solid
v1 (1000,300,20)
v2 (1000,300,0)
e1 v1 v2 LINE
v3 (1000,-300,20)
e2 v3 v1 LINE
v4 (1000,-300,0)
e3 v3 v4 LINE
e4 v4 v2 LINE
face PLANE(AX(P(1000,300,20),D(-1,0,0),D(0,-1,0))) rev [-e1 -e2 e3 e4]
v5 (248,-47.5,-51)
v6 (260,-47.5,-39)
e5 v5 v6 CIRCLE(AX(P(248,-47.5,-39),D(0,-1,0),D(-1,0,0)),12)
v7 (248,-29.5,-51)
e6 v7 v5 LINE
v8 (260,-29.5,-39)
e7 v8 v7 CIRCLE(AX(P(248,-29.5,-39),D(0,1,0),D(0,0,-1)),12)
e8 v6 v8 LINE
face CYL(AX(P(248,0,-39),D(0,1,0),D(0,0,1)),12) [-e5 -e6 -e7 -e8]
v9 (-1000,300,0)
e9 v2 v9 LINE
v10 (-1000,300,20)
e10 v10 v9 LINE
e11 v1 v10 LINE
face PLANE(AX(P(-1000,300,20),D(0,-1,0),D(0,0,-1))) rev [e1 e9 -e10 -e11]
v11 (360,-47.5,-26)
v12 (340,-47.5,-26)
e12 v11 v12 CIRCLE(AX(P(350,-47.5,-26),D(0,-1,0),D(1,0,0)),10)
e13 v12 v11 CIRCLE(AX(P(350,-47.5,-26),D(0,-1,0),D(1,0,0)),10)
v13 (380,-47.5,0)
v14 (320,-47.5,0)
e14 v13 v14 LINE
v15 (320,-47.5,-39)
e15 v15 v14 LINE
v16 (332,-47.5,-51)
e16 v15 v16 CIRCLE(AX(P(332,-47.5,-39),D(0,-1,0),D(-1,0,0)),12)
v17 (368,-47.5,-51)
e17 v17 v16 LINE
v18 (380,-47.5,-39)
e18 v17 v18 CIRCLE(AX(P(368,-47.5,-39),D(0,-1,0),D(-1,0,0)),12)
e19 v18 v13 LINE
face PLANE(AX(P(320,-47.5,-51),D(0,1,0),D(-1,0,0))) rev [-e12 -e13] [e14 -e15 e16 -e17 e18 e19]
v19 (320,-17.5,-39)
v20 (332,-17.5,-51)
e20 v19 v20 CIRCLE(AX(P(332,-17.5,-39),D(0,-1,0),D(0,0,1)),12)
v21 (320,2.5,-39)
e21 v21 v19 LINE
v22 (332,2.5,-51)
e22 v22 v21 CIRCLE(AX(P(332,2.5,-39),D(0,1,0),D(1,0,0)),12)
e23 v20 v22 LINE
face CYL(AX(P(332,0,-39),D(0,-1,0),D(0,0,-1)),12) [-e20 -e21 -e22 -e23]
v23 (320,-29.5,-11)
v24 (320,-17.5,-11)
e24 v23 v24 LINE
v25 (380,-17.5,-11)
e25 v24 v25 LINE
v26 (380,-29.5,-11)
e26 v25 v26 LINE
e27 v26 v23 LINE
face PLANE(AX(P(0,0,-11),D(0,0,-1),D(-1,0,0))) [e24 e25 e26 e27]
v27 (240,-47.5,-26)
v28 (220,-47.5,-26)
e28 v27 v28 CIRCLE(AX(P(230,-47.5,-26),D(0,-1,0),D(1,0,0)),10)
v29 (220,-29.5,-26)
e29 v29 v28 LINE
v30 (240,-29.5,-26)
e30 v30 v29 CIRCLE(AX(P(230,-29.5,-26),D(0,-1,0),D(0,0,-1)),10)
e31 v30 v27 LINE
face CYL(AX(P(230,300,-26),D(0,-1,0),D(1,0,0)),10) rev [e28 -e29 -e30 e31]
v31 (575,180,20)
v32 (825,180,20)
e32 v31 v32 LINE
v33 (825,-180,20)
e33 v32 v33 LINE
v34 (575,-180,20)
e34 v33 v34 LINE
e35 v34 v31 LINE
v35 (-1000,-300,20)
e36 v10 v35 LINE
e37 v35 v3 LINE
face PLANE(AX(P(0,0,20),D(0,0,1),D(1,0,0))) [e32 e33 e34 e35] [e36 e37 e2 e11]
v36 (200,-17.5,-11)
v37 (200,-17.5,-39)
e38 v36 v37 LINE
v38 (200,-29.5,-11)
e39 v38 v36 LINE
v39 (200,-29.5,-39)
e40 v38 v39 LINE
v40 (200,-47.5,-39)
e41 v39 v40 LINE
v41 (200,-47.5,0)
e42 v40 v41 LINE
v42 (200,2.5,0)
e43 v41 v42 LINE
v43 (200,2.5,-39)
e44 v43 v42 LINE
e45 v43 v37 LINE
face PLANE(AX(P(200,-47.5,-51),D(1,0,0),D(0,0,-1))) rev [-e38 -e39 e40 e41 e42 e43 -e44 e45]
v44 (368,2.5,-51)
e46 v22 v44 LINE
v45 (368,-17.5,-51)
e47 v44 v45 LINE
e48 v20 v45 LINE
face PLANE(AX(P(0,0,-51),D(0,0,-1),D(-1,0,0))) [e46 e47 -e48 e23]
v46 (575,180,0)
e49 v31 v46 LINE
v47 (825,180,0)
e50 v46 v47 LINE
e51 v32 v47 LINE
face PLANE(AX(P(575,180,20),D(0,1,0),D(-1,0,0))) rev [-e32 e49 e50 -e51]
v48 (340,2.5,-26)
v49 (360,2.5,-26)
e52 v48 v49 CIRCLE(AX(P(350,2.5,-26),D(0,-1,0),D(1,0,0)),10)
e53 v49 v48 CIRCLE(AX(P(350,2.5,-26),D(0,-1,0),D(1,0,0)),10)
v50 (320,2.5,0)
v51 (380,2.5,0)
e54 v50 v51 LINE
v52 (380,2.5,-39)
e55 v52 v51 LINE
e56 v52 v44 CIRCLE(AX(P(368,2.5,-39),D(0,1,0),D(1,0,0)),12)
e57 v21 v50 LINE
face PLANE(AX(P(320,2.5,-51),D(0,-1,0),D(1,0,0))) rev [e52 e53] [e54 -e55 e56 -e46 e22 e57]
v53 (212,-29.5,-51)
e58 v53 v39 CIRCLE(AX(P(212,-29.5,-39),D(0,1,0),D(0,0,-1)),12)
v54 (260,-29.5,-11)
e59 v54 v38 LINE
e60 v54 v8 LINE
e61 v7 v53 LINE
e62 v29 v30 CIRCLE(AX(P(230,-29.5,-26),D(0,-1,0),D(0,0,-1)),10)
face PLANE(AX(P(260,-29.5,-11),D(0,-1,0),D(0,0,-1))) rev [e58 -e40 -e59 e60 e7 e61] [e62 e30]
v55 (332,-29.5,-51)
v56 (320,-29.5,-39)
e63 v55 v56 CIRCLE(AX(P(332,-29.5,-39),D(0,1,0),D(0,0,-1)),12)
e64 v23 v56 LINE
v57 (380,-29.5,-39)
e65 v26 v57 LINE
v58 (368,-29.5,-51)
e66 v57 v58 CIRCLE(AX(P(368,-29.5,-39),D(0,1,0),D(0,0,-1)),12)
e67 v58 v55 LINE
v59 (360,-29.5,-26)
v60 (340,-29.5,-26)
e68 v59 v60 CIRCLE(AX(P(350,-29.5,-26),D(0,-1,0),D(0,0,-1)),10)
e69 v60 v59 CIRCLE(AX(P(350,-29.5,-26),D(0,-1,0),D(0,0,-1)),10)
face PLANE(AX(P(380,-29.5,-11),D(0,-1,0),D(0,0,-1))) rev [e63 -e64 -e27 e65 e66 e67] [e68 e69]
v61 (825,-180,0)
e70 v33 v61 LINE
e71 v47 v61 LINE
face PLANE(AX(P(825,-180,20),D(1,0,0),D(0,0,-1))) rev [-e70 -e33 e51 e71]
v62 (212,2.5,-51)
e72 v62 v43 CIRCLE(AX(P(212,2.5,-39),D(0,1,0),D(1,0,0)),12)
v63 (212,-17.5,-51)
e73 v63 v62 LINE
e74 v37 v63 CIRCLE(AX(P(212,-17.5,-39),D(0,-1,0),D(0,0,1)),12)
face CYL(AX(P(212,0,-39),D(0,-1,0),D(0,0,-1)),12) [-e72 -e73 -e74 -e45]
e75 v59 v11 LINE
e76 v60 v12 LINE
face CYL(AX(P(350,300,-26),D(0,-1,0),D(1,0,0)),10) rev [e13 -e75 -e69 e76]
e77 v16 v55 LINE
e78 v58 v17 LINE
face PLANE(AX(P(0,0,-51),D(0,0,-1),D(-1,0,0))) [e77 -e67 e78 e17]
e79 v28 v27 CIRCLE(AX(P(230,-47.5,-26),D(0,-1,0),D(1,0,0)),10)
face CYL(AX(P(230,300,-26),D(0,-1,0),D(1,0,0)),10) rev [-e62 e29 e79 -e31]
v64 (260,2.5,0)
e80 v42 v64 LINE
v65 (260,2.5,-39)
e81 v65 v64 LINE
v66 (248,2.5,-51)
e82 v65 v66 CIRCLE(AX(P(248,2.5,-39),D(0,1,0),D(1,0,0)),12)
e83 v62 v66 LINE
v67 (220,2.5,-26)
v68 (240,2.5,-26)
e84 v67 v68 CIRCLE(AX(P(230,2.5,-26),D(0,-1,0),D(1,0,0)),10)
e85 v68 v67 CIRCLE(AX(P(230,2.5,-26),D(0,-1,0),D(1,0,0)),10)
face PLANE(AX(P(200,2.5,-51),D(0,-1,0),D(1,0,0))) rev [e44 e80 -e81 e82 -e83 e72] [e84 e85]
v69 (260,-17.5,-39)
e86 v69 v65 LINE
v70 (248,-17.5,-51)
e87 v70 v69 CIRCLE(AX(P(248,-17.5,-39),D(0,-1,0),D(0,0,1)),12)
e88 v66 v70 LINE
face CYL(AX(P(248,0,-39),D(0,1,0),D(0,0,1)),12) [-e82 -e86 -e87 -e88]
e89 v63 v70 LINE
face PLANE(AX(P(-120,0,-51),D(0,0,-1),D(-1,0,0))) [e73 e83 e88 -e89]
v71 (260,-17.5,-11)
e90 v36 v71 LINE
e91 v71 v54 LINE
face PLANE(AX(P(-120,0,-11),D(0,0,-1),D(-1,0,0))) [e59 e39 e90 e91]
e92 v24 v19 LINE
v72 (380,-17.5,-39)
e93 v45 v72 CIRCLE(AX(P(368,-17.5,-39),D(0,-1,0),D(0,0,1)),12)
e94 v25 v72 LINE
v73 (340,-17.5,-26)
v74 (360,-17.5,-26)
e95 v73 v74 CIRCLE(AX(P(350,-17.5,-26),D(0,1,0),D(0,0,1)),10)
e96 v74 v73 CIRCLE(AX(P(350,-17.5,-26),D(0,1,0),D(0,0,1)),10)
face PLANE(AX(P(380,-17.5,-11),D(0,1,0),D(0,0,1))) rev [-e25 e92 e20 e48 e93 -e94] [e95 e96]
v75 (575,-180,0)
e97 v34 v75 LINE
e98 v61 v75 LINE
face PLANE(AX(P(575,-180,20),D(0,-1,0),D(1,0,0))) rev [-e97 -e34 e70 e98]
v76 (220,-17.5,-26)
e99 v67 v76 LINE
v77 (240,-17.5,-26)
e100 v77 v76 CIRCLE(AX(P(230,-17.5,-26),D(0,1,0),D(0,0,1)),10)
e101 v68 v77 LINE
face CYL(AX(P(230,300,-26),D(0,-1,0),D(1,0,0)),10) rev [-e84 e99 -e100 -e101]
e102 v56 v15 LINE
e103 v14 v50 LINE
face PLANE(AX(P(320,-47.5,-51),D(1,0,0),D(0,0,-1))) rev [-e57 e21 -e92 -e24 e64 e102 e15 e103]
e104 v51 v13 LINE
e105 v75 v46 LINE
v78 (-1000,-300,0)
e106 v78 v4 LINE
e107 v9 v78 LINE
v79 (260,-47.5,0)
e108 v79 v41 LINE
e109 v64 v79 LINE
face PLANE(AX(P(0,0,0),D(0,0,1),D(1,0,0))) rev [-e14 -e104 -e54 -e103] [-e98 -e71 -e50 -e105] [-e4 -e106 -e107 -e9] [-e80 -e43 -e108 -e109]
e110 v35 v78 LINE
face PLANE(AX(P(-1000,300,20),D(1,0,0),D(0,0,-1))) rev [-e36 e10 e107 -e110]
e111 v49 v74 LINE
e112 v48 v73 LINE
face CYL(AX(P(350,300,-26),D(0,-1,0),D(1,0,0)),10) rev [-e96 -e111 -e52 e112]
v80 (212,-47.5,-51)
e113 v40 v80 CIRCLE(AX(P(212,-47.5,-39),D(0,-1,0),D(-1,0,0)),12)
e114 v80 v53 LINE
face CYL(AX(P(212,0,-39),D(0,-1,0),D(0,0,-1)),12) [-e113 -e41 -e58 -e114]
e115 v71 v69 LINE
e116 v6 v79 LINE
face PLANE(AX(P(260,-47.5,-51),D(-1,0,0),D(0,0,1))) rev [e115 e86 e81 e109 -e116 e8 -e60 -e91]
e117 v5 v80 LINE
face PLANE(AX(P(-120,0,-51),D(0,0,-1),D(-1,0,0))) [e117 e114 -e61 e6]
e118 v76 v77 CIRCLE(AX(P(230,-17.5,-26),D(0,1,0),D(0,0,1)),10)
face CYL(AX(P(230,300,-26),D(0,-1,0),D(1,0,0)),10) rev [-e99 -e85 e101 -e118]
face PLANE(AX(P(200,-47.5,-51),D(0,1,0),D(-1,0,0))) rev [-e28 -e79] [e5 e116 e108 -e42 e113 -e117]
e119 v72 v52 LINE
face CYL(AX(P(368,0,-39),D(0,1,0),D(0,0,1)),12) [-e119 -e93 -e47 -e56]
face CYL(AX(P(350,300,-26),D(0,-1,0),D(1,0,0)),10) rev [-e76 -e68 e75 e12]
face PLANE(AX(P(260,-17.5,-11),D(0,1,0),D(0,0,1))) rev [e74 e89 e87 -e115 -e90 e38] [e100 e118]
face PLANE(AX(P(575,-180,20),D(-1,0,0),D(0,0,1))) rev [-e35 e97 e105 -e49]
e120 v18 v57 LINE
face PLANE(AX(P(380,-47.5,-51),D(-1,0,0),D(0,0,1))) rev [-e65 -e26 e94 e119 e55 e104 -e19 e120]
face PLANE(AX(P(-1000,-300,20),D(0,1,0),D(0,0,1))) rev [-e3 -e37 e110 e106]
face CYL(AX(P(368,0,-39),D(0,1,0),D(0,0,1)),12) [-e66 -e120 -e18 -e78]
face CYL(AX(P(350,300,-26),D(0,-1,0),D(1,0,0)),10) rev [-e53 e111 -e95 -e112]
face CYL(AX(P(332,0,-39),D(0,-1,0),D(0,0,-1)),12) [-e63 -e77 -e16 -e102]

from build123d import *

# Parameters (mm, degrees)
SKETCH1_W              = 2000
SKETCH1_H              = 600
BOSS_EXTRUDE1_DEPTH    = 20
SKETCH2_W              = 250
SKETCH2_H              = 360
CUT_EXTRUDE1_DEPTH     = 1045.222198577
SKETCH3_W              = 60
SKETCH3_H              = 50
BOSS_EXTRUDE2_DEPTH    = 51
SKETCH4_W              = 60
SKETCH4_H              = 12
CUT_EXTRUDE2_DEPTH     = 40
FILLET1_R              = 12
SKETCH5_R              = 10
CUT_EXTRUDE3_DEPTH     = 1060.885489098
LPATTERN1_COUNT        = 2
LPATTERN1_PITCH        = 120
FILLET1_OF_LPATTERN1_R = 12


with BuildPart() as part:
    # Sketch1 → Boss-Extrude1 (new body)
    with BuildSketch(Plane.XY):
        Rectangle(SKETCH1_W, SKETCH1_H)
    extrude(amount=BOSS_EXTRUDE1_DEPTH)

    # Sketch2 → Cut-Extrude1 (cut, through all)
    with BuildSketch(Plane(origin=(0, 0, 0), x_dir=(-1, 0, 0), z_dir=(0, 0, -1))):
        with Locations((-700, 0)):
            Rectangle(SKETCH2_W, SKETCH2_H)
    extrude(amount=-CUT_EXTRUDE1_DEPTH, mode=Mode.SUBTRACT)

    # Sketch3 → Boss-Extrude2 (add)
    with BuildSketch(Plane(origin=(0, 0, 0), x_dir=(-1, 0, 0), z_dir=(0, 0, -1))):
        with Locations((-350, -22.5)):
            Rectangle(SKETCH3_W, SKETCH3_H)
    boss_extrude2 = extrude(amount=BOSS_EXTRUDE2_DEPTH)

    # Sketch4 → Cut-Extrude2 (cut)
    with BuildSketch(Plane(origin=(0, 0, -51), x_dir=(-1, 0, 0), z_dir=(0, 0, -1))):
        with Locations((-350, -23.5)):
            Rectangle(SKETCH4_W, SKETCH4_H)
    cut_extrude2 = extrude(amount=-CUT_EXTRUDE2_DEPTH, mode=Mode.SUBTRACT)

    # Fillet1
    fillet1_edges = [part.edges().sort_by_distance(p)[0] for p in [
        (380, -7.5, -51),
        (320, -38.5, -51),
        (380, -38.5, -51),
        (320, -7.5, -51),
    ]]
    fillet(fillet1_edges, radius=FILLET1_R)

    # Sketch5 → Cut-Extrude3 (cut, through all)
    with BuildSketch(Plane.XZ.offset(47.5)):
        with Locations((350, -26)):
            Circle(SKETCH5_R)
    cut_extrude3 = extrude(amount=-CUT_EXTRUDE3_DEPTH, mode=Mode.SUBTRACT)

    # LPattern1: Boss-Extrude2, Cut-Extrude2, Cut-Extrude3 ×2
    with Locations(*[(-i * LPATTERN1_PITCH, 0, 0) for i in range(1, LPATTERN1_COUNT)]):
        add(boss_extrude2)
        add(cut_extrude2, mode=Mode.SUBTRACT)
        add(cut_extrude3, mode=Mode.SUBTRACT)

    # Fillet1 of LPattern1
    fillet1_of_lpattern1_edges = [part.edges().sort_by_distance(p)[0] for p in [
        (260, -7.5, -51),
        (200, -38.5, -51),
        (260, -38.5, -51),
        (200, -7.5, -51),
    ]]
    fillet(fillet1_of_lpattern1_edges, radius=FILLET1_OF_LPATTERN1_R)


solid = part.part
